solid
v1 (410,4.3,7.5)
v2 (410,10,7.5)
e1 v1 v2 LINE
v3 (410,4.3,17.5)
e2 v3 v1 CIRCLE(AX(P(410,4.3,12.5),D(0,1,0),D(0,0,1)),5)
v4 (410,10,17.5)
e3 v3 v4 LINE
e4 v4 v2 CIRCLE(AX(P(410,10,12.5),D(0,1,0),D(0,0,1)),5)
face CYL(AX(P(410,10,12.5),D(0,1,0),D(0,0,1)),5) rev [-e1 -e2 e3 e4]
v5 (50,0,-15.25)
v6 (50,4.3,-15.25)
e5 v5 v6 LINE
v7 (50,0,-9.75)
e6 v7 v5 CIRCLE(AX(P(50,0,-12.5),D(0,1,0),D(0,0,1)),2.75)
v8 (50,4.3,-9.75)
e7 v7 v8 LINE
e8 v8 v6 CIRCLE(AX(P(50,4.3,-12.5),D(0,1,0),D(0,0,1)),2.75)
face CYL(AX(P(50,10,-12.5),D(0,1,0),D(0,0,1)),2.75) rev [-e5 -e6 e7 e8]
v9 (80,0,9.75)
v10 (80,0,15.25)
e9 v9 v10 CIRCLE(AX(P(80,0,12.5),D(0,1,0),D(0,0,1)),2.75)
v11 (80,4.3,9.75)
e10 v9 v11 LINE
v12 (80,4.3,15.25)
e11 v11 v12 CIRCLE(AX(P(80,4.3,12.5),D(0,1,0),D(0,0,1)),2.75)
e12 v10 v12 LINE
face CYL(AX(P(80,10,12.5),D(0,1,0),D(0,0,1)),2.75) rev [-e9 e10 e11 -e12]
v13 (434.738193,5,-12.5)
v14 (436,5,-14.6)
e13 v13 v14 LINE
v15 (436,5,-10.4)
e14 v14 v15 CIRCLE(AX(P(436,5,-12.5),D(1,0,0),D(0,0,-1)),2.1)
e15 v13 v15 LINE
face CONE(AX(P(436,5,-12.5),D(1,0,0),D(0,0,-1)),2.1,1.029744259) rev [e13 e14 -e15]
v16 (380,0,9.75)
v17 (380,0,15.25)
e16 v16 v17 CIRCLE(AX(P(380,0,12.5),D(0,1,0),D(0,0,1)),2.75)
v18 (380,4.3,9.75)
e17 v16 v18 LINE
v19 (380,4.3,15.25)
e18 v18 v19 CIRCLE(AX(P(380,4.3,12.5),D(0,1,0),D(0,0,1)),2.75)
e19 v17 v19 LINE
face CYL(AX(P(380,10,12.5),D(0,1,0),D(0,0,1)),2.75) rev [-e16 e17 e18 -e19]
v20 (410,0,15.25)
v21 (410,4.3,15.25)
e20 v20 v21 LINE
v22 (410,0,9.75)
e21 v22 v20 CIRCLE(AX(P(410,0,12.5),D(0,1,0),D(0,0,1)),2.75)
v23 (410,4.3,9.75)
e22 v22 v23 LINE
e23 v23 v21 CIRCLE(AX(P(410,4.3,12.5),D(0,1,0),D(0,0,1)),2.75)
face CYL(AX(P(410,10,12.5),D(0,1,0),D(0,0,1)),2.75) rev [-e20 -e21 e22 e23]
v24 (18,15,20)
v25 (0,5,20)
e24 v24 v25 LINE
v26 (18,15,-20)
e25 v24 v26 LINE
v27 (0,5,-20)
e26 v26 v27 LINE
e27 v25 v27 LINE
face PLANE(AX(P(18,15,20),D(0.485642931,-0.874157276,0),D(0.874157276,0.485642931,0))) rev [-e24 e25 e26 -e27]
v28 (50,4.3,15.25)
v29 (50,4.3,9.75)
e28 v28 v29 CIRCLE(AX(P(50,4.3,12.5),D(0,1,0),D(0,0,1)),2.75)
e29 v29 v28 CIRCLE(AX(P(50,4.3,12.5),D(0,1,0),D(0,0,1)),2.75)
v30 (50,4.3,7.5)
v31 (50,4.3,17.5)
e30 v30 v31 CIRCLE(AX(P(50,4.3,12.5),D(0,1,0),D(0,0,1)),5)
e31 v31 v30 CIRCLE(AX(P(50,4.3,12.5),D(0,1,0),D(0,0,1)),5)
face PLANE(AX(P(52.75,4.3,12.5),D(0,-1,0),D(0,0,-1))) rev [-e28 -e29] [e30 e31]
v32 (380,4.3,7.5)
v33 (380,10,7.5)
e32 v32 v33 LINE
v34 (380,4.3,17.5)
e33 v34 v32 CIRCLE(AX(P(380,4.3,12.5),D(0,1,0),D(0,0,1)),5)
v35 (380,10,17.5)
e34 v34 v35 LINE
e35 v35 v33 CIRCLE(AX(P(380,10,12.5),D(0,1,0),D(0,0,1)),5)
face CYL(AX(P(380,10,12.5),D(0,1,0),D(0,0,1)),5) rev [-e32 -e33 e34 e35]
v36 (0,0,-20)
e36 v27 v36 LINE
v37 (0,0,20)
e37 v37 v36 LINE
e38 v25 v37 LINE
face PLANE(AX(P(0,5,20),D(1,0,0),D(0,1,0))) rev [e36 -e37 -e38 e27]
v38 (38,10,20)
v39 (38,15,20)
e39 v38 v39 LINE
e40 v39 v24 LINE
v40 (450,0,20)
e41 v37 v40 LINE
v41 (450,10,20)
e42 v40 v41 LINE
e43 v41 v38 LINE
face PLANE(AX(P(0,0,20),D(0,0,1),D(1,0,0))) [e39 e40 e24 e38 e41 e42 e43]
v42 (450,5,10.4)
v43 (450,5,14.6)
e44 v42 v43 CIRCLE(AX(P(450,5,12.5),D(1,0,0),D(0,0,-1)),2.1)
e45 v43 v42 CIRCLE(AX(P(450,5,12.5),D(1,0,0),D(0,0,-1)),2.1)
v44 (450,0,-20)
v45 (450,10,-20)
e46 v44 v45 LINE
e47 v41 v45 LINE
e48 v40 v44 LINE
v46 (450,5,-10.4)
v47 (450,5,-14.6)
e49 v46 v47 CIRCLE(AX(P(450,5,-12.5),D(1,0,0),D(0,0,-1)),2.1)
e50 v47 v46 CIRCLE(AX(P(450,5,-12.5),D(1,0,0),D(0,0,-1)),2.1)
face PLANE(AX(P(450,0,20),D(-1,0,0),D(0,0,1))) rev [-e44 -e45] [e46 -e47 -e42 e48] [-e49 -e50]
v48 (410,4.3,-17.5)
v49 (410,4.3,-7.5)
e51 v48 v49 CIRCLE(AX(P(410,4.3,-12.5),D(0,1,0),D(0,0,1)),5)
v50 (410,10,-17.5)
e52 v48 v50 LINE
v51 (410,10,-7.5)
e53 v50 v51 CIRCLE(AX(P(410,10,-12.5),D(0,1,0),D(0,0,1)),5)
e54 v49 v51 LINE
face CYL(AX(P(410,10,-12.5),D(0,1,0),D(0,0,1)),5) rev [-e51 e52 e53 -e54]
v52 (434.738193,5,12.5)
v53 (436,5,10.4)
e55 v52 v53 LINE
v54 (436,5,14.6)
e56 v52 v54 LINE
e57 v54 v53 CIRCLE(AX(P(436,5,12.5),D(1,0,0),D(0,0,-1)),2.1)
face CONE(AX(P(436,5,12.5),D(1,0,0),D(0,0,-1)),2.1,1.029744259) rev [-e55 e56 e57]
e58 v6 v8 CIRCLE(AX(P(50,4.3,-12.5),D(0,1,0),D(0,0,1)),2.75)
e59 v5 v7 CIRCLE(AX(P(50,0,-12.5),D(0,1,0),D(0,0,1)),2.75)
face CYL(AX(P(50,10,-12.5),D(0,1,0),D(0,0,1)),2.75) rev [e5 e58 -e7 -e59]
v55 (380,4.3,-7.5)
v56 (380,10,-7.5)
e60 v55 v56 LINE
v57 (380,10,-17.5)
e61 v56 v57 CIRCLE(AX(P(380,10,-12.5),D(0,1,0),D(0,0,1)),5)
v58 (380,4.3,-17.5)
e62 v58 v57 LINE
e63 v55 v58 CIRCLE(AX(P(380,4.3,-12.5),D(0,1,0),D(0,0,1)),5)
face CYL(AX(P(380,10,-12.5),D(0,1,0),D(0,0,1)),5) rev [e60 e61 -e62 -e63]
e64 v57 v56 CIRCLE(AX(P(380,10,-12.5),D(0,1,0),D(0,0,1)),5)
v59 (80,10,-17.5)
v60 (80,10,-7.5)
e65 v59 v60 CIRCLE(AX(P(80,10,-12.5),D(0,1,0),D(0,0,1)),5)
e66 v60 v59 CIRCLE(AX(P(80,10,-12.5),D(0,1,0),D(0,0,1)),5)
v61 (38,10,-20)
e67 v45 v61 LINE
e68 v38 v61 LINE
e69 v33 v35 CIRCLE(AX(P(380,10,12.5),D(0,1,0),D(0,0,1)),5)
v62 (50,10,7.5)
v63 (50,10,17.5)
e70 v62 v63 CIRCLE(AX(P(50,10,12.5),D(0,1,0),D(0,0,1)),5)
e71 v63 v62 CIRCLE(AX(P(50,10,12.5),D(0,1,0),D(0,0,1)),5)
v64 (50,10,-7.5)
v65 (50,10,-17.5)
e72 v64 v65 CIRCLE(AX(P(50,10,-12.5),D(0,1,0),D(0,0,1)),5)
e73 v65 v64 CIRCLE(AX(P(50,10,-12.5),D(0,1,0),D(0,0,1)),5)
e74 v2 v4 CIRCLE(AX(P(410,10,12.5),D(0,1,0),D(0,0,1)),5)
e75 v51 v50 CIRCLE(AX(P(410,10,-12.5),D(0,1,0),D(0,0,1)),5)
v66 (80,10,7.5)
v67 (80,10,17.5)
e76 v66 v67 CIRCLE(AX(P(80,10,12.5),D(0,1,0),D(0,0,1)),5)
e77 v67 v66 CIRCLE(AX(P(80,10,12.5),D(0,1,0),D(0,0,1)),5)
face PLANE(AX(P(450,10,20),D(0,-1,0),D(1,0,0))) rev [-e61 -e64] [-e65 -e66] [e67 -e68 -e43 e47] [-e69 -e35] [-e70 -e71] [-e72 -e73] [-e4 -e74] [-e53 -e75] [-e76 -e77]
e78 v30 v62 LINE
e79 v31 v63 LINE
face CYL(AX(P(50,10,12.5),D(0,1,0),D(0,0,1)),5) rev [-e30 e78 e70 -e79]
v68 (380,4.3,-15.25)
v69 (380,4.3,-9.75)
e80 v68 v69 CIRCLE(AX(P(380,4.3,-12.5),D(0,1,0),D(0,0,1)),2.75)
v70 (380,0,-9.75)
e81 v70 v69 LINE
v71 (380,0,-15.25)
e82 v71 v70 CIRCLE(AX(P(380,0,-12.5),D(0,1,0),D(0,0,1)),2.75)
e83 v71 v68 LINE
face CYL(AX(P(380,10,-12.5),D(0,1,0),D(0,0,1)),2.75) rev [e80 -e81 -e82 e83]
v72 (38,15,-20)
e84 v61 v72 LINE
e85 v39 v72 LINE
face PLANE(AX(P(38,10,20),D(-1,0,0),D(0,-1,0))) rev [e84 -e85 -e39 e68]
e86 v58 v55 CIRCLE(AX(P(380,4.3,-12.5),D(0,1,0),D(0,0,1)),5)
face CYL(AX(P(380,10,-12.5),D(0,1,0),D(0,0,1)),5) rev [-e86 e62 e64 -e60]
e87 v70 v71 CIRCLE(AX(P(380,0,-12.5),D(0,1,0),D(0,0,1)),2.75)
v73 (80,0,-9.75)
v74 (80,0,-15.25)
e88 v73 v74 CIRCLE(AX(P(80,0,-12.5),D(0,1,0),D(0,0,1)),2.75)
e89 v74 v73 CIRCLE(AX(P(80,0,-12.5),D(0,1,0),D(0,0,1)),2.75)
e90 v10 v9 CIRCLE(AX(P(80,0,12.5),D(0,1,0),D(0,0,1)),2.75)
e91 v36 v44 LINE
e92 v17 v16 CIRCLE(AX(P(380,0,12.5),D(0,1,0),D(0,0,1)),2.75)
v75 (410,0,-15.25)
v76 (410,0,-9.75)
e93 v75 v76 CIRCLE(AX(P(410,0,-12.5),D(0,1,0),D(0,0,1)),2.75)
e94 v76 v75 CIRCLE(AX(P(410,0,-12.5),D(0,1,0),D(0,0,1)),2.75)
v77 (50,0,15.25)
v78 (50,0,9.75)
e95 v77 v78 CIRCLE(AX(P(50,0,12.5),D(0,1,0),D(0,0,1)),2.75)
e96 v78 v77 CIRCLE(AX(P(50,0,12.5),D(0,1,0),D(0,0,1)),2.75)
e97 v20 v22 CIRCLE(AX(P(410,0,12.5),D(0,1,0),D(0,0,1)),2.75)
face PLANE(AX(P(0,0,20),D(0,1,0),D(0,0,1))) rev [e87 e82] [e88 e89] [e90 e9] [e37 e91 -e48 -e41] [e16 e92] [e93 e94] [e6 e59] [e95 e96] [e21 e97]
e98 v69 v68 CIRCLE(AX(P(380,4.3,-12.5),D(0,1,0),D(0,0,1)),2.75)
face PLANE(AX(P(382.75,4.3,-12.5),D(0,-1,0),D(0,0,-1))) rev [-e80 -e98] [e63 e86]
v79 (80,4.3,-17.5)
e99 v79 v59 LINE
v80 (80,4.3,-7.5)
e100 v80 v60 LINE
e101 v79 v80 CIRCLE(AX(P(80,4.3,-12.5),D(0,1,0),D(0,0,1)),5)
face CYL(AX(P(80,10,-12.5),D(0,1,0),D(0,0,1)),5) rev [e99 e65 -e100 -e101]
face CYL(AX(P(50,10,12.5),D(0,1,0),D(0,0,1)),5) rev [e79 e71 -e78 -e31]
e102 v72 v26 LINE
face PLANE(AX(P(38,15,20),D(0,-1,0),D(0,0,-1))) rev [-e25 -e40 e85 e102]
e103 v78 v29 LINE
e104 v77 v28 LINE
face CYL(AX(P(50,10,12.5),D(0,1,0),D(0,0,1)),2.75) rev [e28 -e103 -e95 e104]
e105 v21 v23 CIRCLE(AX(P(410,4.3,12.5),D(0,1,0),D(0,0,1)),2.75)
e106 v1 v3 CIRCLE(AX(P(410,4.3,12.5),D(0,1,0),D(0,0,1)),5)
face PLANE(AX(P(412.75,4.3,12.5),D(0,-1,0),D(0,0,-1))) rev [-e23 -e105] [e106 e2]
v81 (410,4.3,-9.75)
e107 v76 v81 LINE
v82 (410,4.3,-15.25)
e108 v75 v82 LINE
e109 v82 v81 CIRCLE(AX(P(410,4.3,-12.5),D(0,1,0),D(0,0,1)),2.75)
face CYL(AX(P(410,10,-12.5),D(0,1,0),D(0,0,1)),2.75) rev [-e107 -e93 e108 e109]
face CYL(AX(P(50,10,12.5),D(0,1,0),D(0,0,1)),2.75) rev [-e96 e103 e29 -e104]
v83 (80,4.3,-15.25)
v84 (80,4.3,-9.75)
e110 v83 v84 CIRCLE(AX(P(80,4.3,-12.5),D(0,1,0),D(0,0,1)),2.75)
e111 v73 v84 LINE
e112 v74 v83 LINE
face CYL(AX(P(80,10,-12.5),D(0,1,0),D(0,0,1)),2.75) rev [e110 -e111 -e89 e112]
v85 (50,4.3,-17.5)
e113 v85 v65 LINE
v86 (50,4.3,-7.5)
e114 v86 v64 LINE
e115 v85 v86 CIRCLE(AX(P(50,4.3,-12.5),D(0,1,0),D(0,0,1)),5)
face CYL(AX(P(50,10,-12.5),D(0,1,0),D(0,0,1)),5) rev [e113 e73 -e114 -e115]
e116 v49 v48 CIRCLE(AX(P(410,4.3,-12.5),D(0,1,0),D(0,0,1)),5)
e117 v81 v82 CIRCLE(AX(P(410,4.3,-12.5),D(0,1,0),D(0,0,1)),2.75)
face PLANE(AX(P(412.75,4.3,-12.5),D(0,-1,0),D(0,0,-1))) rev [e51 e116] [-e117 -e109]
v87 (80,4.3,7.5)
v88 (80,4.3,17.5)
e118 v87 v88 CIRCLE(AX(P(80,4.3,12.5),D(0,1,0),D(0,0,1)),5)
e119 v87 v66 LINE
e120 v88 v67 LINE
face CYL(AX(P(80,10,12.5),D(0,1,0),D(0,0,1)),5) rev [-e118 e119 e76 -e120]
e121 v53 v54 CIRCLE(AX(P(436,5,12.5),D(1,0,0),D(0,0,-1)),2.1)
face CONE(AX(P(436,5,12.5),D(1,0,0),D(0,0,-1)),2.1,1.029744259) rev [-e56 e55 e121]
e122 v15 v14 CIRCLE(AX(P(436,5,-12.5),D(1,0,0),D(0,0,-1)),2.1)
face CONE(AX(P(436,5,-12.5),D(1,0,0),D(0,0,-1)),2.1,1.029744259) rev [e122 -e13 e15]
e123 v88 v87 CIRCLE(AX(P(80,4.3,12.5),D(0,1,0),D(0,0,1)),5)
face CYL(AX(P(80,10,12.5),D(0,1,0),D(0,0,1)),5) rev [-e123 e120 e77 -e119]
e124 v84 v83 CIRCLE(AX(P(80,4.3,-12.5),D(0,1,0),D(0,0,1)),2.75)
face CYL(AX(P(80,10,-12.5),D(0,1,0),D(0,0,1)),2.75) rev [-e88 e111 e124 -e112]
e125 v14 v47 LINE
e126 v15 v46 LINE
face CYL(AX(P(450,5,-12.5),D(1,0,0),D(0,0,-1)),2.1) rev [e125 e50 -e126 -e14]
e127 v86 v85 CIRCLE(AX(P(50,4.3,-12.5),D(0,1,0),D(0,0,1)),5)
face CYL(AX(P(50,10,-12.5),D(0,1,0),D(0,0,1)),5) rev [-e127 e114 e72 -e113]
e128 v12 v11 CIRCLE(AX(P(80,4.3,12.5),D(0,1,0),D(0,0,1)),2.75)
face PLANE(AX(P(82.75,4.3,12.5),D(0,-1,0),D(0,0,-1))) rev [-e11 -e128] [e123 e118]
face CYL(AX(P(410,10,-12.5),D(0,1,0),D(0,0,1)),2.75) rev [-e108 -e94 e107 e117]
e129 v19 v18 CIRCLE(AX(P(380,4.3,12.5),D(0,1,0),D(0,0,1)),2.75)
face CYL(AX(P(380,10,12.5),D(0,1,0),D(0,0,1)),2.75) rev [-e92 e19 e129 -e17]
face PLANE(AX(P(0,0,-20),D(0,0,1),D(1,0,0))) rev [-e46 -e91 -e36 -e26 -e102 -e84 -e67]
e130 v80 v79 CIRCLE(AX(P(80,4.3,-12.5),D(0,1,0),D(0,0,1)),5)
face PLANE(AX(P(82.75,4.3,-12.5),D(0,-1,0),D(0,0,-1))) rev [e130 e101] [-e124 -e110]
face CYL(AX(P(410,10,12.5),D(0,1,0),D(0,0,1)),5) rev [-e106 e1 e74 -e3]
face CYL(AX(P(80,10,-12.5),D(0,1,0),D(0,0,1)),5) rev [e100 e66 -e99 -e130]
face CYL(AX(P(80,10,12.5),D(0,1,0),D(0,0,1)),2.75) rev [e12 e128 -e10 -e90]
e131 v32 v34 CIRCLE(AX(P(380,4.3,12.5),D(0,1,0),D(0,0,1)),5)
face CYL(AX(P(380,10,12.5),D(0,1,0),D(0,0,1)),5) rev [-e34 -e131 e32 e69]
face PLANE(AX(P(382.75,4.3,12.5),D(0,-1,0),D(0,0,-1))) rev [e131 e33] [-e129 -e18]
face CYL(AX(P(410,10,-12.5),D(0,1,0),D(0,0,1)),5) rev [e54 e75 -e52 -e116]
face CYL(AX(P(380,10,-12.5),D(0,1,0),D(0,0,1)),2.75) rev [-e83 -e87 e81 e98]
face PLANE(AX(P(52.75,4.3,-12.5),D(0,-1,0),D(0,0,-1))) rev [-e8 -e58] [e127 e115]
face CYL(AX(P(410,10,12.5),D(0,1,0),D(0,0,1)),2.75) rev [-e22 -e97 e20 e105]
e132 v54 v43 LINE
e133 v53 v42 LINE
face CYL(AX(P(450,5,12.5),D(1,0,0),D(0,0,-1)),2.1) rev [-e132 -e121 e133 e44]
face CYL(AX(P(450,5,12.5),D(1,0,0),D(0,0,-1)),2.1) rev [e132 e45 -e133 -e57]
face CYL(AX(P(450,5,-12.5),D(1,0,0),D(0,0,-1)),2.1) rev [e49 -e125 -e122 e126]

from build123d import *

# Parameters (mm, degrees)
EXTRUDE_1_DEPTH           = 20
HOLE_WIZARD_1_D           = 5.5
HOLE_WIZARD_1_DEPTH       = 14
HOLE_WIZARD_1_CBORE_D     = 10
HOLE_WIZARD_1_CBORE_DEPTH = 5.7
HOLE_WIZARD_1_TIP         = 1.652366702
HOLE_WIZARD_M5_1_D        = 4.2
HOLE_WIZARD_M5_1_DEPTH    = 14
HOLE_WIZARD_M5_1_TIP      = 1.2618073


with BuildPart() as part:
    # 草图1 → 凸台-拉伸1 (new, symmetric)
    with BuildSketch(Plane.XY):
        Polygon((0, 0), (450, 0), (450, 10), (38, 10), (38, 15), (18, 15), (0, 5), align=None)
    extrude(amount=EXTRUDE_1_DEPTH, both=True)

    # 打孔尺寸(%根据)内六角圆柱头螺钉的类型1
    with Locations(Plane(origin=(0, 10, 0), x_dir=(1, 0, 0), z_dir=(0, 1, 0))):
        with Locations((50, 12.5), (80, 12.5), (50, -12.5), (80, -12.5), (380, -12.5), (410, -12.5), (380, 12.5), (410, 12.5)):
            CounterBoreHole(HOLE_WIZARD_1_D / 2, HOLE_WIZARD_1_CBORE_D / 2, HOLE_WIZARD_1_CBORE_DEPTH, depth=HOLE_WIZARD_1_DEPTH)
            with Locations((0, 0, -(HOLE_WIZARD_1_DEPTH + HOLE_WIZARD_1_TIP / 2))):  # 118° drill point
                Cone(0, HOLE_WIZARD_1_D / 2, HOLE_WIZARD_1_TIP, mode=Mode.SUBTRACT)

    # M5 螺纹孔1
    with Locations(Plane(origin=(450, 0, 0), x_dir=(0, 0, -1), z_dir=(1, 0, 0))):
        with Locations((-12.5, 5), (12.5, 5)):
            Hole(HOLE_WIZARD_M5_1_D / 2, depth=HOLE_WIZARD_M5_1_DEPTH)
            with Locations((0, 0, -(HOLE_WIZARD_M5_1_DEPTH + HOLE_WIZARD_M5_1_TIP / 2))):  # 118° drill point
                Cone(0, HOLE_WIZARD_M5_1_D / 2, HOLE_WIZARD_M5_1_TIP, mode=Mode.SUBTRACT)


solid = part.part
